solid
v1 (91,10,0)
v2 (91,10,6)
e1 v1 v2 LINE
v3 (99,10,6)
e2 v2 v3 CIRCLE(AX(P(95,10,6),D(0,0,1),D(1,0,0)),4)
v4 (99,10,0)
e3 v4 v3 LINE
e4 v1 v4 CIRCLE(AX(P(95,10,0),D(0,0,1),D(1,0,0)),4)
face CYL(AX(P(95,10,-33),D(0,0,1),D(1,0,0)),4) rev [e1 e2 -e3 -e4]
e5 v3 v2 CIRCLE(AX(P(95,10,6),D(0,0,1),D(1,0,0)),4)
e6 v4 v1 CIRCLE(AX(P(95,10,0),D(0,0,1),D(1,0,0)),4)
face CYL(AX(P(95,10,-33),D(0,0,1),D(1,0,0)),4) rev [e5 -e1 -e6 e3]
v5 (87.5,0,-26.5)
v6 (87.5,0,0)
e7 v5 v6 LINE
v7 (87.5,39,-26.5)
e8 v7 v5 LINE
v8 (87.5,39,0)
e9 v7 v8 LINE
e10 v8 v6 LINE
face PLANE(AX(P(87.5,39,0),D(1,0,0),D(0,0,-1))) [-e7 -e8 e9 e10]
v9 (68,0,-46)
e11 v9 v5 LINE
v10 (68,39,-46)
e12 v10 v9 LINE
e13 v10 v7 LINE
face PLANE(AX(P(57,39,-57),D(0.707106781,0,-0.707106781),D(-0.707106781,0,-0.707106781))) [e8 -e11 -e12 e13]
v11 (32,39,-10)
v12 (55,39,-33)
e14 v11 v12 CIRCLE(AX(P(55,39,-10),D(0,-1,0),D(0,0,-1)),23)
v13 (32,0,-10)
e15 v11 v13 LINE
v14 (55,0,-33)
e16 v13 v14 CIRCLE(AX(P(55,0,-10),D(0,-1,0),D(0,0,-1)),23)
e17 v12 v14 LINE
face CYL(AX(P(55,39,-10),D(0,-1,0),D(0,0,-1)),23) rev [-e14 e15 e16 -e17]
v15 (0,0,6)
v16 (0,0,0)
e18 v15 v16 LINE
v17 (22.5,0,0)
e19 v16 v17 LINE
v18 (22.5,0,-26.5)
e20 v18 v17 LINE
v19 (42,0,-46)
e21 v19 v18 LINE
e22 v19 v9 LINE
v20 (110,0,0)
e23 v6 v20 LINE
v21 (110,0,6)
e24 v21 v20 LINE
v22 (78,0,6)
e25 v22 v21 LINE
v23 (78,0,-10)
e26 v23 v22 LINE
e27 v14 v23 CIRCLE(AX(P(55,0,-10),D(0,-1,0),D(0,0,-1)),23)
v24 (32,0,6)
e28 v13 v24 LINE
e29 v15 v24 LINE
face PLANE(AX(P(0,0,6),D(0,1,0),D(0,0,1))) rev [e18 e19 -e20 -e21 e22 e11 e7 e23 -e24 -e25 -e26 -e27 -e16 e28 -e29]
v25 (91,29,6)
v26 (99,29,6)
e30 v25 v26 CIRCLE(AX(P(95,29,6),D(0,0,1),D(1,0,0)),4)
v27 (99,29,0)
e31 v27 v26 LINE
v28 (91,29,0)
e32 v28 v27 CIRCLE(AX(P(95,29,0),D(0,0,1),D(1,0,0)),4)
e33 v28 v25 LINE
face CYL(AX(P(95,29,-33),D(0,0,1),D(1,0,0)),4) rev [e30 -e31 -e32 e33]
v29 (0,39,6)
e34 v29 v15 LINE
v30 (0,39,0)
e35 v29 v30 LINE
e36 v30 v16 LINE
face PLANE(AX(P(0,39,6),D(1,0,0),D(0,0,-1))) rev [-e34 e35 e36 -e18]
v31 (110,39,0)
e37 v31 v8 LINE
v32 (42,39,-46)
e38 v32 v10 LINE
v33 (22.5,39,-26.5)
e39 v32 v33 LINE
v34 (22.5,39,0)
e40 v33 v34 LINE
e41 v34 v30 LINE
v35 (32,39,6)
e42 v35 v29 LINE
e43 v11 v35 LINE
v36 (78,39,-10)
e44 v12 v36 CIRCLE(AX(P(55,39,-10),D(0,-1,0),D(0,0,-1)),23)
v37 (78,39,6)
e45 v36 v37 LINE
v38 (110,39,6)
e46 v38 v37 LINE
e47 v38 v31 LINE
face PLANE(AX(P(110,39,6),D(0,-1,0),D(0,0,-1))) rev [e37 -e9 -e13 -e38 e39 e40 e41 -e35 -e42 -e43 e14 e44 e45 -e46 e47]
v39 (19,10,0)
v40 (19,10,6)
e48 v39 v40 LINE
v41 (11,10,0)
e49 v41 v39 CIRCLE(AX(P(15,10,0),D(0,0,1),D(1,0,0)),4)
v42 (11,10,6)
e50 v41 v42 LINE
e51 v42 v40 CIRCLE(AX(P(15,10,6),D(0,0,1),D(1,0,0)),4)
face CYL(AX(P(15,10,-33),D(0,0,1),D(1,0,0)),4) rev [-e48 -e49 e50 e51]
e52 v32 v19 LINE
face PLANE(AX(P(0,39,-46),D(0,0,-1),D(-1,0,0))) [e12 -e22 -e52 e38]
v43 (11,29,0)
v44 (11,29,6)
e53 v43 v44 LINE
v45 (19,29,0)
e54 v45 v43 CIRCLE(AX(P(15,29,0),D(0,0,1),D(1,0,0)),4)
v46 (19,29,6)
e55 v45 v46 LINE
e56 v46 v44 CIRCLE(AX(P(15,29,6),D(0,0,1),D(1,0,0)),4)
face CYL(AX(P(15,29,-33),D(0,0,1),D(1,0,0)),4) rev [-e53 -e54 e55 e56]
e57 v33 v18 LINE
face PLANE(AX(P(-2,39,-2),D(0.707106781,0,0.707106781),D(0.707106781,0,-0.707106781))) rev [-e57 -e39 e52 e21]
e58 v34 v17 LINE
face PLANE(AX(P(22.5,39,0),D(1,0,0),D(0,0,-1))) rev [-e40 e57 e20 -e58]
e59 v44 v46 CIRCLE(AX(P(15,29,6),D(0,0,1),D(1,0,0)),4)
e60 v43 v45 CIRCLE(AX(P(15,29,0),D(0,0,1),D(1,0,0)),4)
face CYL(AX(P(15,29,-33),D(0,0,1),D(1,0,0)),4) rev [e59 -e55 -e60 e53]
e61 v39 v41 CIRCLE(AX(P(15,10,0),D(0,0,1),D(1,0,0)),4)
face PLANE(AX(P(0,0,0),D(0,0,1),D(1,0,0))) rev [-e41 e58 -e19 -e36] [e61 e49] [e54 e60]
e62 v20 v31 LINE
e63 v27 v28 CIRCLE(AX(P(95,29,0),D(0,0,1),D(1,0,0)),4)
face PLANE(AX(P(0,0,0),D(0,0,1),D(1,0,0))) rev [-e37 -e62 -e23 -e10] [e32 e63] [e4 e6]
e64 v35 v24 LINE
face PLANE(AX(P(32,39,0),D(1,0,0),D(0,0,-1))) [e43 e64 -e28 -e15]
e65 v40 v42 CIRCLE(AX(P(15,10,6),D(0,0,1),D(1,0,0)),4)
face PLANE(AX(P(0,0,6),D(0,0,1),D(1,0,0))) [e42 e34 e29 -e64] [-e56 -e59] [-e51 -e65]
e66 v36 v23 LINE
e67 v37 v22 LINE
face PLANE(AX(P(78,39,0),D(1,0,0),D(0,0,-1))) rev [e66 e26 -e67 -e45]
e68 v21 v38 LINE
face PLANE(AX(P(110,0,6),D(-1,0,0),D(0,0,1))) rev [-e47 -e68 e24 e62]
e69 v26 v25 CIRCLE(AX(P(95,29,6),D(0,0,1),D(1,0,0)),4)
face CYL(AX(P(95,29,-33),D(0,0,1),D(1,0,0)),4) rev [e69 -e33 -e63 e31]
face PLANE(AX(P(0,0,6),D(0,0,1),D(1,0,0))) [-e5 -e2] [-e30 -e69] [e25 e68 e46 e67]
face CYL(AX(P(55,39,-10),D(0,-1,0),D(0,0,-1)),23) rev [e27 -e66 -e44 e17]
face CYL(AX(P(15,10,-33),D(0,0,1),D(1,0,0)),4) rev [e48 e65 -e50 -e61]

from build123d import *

# Parameters (mm, degrees)
BASE_PLATE_SKETCH_W       = 110
BASE_PLATE_SKETCH_H       = 39
BASE_PLATE_110X39X6_DEPTH = 6
SADDLE_BODY_39_DEPTH      = 39
SADDLE_CUTOUT_SKETCH_W    = 46
SADDLE_CUTOUT_SKETCH_H    = 6
SADDLE_CUTOUT_DEPTH       = 39
FLANGE_HOLES_SKETCH_R     = 4
FLANGE_HOLES_4X_8_DEPTH   = 39


with BuildPart() as part:
    # Base Plate Sketch → Base Plate 110x39x6 (new body)
    with BuildSketch(Plane.XY):
        with Locations((55, 19.5)):
            Rectangle(BASE_PLATE_SKETCH_W, BASE_PLATE_SKETCH_H)
    extrude(amount=BASE_PLATE_110X39X6_DEPTH)

    # Saddle Body Profile → Saddle Body 39 (add)
    with BuildSketch(Plane.XZ):
        with BuildLine():
            Line((32, -10), (32, 0))
            Line((32, 0), (22.5, 0))
            Line((22.5, 0), (22.5, -26.5))
            Line((22.5, -26.5), (42, -46))
            Line((42, -46), (55, -46))
            Line((55, -46), (55, -33))
            ThreePointArc((55, -33), (38.736544033, -26.263455967), (32, -10))
        make_face()
        with BuildLine():
            Line((87.5, 0), (78, 0))
            Line((78, 0), (78, -10))
            ThreePointArc((78, -10), (71.263455967, -26.263455967), (55, -33))
            Line((55, -33), (55, -46))
            Line((55, -46), (68, -46))
            Line((68, -46), (87.5, -26.5))
            Line((87.5, -26.5), (87.5, 0))
        make_face()
    extrude(amount=-SADDLE_BODY_39_DEPTH)

    # Saddle Cutout Sketch → Saddle Cutout (cut)
    with BuildSketch(Plane.XZ):
        with Locations((55, 3)):
            Rectangle(SADDLE_CUTOUT_SKETCH_W, SADDLE_CUTOUT_SKETCH_H)
    extrude(amount=-SADDLE_CUTOUT_DEPTH, mode=Mode.SUBTRACT)

    # Flange Holes Sketch → Flange Holes 4xØ8 (cut)
    with BuildSketch(Plane.XY.offset(6)):
        with Locations((15, 29)):
            Circle(FLANGE_HOLES_SKETCH_R)
        with Locations((15, 10)):
            Circle(FLANGE_HOLES_SKETCH_R)
        with Locations((95, 29)):
            Circle(FLANGE_HOLES_SKETCH_R)
        with Locations((95, 10)):
            Circle(FLANGE_HOLES_SKETCH_R)
    extrude(amount=-FLANGE_HOLES_4X_8_DEPTH, mode=Mode.SUBTRACT)


solid = part.part
